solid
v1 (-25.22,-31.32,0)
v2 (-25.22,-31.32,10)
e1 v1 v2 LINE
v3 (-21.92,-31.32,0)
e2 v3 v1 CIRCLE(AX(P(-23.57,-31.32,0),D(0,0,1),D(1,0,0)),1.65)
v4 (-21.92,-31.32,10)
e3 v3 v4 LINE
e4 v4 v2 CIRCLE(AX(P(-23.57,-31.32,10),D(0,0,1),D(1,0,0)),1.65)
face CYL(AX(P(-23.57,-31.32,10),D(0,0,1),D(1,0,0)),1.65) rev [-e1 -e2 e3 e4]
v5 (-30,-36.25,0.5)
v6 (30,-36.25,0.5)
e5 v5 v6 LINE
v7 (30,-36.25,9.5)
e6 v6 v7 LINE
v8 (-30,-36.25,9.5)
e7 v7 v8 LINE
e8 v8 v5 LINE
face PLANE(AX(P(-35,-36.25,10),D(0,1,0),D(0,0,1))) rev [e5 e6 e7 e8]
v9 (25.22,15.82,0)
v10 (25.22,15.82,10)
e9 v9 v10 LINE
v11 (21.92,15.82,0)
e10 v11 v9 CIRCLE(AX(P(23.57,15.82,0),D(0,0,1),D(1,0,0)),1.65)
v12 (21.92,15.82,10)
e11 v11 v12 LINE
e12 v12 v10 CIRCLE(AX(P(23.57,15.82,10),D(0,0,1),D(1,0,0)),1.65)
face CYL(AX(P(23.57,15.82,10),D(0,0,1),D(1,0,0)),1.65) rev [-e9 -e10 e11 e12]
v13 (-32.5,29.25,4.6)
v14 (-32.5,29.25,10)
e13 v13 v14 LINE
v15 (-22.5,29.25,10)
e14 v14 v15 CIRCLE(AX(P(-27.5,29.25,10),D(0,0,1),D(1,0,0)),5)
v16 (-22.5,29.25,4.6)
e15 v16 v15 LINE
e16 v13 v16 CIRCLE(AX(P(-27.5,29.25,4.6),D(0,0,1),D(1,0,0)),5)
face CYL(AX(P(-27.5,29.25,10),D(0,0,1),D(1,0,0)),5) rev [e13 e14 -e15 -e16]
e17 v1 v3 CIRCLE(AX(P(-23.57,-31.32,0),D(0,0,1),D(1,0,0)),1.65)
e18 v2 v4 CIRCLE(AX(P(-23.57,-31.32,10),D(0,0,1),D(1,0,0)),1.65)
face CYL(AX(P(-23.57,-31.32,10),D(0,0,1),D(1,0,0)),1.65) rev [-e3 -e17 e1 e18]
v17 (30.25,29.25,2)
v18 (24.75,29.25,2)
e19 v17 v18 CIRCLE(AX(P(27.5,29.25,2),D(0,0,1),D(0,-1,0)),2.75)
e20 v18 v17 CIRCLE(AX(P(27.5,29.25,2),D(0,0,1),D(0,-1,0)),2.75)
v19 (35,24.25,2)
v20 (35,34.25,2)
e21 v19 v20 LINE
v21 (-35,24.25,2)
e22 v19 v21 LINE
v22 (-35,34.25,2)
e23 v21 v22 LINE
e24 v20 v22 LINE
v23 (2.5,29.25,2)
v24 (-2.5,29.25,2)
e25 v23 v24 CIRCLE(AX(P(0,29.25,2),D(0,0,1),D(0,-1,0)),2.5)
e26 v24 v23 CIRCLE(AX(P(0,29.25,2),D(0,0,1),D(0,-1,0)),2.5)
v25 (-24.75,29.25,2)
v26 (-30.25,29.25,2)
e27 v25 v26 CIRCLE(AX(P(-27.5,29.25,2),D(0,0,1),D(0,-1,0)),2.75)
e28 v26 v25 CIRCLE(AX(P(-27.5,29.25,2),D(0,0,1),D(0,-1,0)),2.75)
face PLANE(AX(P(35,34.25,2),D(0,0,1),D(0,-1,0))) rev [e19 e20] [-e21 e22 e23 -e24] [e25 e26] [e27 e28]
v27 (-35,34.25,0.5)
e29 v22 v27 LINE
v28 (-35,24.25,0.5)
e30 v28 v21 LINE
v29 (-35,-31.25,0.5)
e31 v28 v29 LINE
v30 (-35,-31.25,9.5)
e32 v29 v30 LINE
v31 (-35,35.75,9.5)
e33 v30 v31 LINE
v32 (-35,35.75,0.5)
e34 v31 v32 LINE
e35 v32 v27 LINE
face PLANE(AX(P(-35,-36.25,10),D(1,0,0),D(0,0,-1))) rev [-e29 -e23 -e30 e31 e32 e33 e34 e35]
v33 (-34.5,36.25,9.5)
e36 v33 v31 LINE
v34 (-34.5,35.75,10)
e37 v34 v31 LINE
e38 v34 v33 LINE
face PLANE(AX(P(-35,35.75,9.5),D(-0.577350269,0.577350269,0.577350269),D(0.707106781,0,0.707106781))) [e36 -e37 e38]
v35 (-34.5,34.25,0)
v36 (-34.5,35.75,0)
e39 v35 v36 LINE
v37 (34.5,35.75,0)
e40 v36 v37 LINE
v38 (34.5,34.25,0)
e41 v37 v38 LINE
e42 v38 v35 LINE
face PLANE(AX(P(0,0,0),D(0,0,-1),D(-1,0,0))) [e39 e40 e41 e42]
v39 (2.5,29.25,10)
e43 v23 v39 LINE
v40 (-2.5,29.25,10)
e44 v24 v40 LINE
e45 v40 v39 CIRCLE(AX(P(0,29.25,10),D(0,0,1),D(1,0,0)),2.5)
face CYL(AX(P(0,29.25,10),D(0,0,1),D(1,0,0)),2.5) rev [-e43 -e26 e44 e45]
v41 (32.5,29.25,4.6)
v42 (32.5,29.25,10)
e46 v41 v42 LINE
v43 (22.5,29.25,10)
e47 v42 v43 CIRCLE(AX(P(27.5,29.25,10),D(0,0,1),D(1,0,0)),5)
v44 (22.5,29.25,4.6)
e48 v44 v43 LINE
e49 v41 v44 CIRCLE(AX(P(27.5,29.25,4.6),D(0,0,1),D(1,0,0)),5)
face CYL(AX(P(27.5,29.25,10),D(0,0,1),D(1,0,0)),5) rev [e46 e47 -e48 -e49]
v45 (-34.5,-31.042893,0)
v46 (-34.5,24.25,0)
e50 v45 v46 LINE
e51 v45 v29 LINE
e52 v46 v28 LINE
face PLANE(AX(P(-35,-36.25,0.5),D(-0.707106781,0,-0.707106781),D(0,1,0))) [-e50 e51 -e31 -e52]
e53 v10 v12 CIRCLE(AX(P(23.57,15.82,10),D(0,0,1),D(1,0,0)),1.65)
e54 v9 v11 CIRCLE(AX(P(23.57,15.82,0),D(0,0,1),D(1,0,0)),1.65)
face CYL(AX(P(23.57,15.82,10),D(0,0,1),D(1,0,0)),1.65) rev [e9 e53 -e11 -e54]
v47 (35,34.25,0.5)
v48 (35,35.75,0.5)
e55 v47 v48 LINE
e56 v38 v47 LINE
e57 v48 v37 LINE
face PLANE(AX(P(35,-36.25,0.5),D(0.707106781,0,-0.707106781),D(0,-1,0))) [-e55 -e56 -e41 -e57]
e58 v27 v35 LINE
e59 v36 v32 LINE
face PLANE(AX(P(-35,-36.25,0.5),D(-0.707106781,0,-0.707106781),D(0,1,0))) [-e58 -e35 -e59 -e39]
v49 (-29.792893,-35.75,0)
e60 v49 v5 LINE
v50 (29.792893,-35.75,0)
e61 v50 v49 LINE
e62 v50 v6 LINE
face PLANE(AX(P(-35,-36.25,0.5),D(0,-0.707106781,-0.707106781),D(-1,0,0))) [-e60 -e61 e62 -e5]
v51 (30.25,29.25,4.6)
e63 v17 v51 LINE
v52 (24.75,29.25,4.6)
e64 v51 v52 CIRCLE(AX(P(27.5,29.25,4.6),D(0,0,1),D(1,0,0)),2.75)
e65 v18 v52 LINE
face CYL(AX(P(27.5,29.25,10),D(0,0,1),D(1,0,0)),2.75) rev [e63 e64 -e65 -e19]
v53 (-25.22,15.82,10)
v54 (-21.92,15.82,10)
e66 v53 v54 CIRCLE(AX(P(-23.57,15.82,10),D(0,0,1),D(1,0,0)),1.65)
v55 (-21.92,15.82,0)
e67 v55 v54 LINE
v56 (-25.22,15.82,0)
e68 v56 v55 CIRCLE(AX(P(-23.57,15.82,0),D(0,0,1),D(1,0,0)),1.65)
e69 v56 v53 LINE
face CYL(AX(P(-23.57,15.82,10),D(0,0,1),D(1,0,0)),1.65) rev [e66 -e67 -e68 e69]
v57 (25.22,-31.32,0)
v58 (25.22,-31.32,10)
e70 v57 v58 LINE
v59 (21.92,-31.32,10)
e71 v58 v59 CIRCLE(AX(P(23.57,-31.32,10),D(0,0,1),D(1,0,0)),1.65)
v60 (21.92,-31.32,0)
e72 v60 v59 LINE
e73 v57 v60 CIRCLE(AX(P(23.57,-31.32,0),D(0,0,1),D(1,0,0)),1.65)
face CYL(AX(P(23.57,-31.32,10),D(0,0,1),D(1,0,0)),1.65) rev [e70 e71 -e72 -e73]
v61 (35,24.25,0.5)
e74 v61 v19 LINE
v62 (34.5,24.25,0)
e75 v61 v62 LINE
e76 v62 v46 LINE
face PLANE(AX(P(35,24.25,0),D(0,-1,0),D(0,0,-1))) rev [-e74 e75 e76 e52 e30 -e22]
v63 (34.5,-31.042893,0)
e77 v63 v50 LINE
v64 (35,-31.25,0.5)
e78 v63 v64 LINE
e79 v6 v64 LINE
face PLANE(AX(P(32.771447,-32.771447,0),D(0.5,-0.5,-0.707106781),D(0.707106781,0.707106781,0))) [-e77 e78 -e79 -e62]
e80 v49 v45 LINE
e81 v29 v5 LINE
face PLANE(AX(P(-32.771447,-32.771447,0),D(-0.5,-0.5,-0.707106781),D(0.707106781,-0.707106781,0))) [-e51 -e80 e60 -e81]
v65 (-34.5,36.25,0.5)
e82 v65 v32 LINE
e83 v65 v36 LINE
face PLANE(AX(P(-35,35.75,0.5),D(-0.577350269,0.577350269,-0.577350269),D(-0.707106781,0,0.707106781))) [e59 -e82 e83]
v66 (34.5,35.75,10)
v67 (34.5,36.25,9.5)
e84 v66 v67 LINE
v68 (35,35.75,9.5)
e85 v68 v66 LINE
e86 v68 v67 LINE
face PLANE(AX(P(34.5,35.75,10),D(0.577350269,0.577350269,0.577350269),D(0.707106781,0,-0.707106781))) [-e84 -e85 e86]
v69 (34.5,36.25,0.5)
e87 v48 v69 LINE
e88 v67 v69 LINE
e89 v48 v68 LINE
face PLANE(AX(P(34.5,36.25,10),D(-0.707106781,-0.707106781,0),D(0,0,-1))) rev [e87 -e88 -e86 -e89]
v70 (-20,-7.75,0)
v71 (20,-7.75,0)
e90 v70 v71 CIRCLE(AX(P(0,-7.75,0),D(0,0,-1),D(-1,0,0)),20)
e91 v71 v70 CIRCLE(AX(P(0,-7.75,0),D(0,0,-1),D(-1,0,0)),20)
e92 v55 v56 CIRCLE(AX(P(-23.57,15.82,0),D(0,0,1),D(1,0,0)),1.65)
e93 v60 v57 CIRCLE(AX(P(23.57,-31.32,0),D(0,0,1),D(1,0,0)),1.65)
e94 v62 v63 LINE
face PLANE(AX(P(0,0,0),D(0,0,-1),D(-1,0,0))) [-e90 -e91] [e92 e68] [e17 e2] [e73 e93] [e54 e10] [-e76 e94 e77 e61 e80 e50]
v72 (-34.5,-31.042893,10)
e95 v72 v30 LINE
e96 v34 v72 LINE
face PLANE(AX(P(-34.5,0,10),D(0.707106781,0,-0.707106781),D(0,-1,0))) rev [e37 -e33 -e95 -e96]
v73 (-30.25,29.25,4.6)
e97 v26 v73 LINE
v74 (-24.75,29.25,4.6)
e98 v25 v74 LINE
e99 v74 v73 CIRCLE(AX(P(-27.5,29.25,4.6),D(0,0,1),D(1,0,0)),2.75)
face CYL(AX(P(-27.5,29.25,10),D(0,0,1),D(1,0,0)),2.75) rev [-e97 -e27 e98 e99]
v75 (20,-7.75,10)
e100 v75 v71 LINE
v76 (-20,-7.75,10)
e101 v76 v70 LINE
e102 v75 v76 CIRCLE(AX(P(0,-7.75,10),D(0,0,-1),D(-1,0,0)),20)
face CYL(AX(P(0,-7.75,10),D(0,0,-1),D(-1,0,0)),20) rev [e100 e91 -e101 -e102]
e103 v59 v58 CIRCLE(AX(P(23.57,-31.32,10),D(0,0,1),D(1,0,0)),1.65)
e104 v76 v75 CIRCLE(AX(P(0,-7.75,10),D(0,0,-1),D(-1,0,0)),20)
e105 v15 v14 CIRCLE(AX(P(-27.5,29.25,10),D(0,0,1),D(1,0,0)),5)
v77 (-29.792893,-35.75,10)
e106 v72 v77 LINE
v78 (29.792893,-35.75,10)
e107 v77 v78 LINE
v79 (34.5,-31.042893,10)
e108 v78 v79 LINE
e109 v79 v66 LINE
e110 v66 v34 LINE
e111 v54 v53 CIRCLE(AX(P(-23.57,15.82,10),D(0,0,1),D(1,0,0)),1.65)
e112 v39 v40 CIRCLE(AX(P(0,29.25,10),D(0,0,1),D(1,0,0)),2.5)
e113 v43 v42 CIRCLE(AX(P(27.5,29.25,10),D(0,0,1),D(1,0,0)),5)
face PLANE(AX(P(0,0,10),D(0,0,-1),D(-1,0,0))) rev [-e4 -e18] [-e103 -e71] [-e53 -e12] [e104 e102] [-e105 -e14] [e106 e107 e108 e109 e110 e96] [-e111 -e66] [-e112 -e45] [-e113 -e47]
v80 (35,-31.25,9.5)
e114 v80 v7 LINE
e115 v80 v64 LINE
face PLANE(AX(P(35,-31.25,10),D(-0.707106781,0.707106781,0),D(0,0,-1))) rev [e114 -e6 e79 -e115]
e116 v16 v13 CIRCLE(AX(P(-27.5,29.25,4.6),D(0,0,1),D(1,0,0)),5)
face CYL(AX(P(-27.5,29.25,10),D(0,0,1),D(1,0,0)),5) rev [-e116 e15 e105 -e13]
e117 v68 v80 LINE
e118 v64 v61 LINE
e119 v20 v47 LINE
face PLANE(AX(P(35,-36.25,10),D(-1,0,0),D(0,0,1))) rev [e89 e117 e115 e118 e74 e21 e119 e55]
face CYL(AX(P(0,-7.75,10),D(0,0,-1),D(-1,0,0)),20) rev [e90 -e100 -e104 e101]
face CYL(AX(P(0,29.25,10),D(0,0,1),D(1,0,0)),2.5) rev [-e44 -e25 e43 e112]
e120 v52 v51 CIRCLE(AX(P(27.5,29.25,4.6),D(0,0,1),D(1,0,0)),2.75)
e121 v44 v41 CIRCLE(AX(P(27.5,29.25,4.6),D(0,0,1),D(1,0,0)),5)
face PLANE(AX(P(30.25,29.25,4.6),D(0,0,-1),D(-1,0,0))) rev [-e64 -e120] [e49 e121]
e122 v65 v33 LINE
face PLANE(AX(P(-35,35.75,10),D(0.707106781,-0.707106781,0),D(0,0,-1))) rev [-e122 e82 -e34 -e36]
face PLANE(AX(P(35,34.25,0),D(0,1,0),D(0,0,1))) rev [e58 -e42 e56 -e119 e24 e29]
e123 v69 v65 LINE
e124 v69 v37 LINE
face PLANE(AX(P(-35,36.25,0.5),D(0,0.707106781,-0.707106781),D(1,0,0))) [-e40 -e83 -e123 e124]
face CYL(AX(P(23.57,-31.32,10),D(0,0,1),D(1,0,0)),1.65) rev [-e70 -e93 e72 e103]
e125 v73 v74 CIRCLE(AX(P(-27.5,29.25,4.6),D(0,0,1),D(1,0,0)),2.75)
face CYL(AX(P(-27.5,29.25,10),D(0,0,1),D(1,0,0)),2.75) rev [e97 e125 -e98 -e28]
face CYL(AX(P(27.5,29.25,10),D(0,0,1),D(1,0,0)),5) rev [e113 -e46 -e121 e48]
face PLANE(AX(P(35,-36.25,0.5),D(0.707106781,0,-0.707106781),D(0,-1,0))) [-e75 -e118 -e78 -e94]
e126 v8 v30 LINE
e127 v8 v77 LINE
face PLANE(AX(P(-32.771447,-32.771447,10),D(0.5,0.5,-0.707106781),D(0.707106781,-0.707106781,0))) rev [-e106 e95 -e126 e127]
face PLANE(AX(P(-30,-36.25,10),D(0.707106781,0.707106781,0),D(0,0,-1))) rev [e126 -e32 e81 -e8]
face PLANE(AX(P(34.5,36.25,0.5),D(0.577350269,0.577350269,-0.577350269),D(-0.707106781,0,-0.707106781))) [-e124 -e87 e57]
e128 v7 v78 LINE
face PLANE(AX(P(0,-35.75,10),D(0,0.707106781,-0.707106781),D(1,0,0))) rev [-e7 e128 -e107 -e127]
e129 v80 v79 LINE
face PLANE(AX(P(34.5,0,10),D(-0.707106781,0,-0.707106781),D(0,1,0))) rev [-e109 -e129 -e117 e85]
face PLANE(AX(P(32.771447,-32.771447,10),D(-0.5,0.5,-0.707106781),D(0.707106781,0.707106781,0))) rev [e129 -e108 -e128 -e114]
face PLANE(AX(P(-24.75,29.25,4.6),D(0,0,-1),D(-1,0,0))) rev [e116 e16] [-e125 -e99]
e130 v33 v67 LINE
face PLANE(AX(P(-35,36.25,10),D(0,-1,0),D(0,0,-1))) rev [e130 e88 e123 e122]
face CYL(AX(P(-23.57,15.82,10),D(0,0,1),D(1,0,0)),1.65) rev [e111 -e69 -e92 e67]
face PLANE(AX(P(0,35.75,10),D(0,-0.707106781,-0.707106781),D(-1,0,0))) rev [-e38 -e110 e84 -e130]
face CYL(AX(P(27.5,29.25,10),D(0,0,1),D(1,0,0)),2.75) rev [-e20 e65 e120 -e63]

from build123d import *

# Parameters (mm, degrees)
SKETCH_1_W                   = 70
SKETCH_1_H                   = 72.5
EXTRUDE_1_DEPTH              = 10
SKETCH_2_W                   = 2
SKETCH_2_H                   = 10
CUT_EXTRUDE_1_DEPTH          = 80.461075377
HOLE_WIZARD_M5_1_D           = 5.5
HOLE_WIZARD_M5_1_CBORE_D     = 10
HOLE_WIZARD_M5_1_CBORE_DEPTH = 5.4
MM_1_D                       = 5
HOLE_WIZARD_M4_1_D           = 3.3
SKETCH_9_R                   = 20
CUT_EXTRUDE_2_DEPTH          = 52.37180647
CHAMFER_1_SIZE               = 5
CHAMFER_2_SIZE               = 0.5


with BuildPart() as part:
    # 草图1 → 凸台-拉伸1 (new body)
    with BuildSketch(Plane.XY):
        Rectangle(SKETCH_1_W, SKETCH_1_H)
    extrude(amount=EXTRUDE_1_DEPTH)

    # 草图2 → 切除-拉伸1 (cut, through all)
    with BuildSketch(Plane.ZY.offset(35)):
        with Locations((1, 29.25)):
            Rectangle(SKETCH_2_W, SKETCH_2_H)
    extrude(amount=-CUT_EXTRUDE_1_DEPTH, mode=Mode.SUBTRACT)

    # M5 六角凹头螺钉的柱形沉头孔1 (through all)
    with Locations(Plane.XY.offset(10)):
        with Locations((27.5, 29.25), (-27.5, 29.25)):
            CounterBoreHole(HOLE_WIZARD_M5_1_D / 2, HOLE_WIZARD_M5_1_CBORE_D / 2, HOLE_WIZARD_M5_1_CBORE_DEPTH)

    # 大小mm 暗销孔1 (through all)
    with Locations(Plane.XY.offset(10)):
        with Locations((0, 29.25)):
            Hole(MM_1_D / 2)

    # M4 螺纹孔1 (through all)
    with Locations(Plane.XY.offset(10)):
        with Locations((-23.57, 15.82), (-23.57, -31.32), (23.57, -31.32), (23.57, 15.82)):
            Hole(HOLE_WIZARD_M4_1_D / 2)

    # 草图9 → 切除-拉伸2 (cut, through all)
    with BuildSketch(Plane(origin=(0, 0, 0), x_dir=(-1, 0, 0), z_dir=(0, 0, -1))):
        with Locations((0, -7.75)):
            Circle(SKETCH_9_R)
    extrude(amount=-CUT_EXTRUDE_2_DEPTH, mode=Mode.SUBTRACT)

    # 倒角1
    chamfer_1_edges = [part.edges().sort_by_distance(p)[0] for p in [
        (35, -36.25, 5),
        (-35, -36.25, 5),
    ]]
    chamfer(chamfer_1_edges, length=CHAMFER_1_SIZE)

    # 倒角2
    chamfer_2_edges = [part.edges().sort_by_distance(p)[0] for p in [
        (35, 2.5, 10),
        (35, -3.5, 0),
        (0, -36.25, 0),
        (-32.5, -33.75, 0),
        (32.5, -33.75, 0),
        (0, -36.25, 10),
        (-32.5, -33.75, 10),
        (32.5, -33.75, 10),
        (-35, 2.5, 10),
        (35, 35.25, 0),
        (-35, -3.5, 0),
        (-35, 35.25, 0),
        (0, 36.25, 0),
        (-35, 36.25, 5),
        (35, 36.25, 5),
        (0, 36.25, 10),
    ]]
    chamfer(chamfer_2_edges, length=CHAMFER_2_SIZE)


solid = part.part
